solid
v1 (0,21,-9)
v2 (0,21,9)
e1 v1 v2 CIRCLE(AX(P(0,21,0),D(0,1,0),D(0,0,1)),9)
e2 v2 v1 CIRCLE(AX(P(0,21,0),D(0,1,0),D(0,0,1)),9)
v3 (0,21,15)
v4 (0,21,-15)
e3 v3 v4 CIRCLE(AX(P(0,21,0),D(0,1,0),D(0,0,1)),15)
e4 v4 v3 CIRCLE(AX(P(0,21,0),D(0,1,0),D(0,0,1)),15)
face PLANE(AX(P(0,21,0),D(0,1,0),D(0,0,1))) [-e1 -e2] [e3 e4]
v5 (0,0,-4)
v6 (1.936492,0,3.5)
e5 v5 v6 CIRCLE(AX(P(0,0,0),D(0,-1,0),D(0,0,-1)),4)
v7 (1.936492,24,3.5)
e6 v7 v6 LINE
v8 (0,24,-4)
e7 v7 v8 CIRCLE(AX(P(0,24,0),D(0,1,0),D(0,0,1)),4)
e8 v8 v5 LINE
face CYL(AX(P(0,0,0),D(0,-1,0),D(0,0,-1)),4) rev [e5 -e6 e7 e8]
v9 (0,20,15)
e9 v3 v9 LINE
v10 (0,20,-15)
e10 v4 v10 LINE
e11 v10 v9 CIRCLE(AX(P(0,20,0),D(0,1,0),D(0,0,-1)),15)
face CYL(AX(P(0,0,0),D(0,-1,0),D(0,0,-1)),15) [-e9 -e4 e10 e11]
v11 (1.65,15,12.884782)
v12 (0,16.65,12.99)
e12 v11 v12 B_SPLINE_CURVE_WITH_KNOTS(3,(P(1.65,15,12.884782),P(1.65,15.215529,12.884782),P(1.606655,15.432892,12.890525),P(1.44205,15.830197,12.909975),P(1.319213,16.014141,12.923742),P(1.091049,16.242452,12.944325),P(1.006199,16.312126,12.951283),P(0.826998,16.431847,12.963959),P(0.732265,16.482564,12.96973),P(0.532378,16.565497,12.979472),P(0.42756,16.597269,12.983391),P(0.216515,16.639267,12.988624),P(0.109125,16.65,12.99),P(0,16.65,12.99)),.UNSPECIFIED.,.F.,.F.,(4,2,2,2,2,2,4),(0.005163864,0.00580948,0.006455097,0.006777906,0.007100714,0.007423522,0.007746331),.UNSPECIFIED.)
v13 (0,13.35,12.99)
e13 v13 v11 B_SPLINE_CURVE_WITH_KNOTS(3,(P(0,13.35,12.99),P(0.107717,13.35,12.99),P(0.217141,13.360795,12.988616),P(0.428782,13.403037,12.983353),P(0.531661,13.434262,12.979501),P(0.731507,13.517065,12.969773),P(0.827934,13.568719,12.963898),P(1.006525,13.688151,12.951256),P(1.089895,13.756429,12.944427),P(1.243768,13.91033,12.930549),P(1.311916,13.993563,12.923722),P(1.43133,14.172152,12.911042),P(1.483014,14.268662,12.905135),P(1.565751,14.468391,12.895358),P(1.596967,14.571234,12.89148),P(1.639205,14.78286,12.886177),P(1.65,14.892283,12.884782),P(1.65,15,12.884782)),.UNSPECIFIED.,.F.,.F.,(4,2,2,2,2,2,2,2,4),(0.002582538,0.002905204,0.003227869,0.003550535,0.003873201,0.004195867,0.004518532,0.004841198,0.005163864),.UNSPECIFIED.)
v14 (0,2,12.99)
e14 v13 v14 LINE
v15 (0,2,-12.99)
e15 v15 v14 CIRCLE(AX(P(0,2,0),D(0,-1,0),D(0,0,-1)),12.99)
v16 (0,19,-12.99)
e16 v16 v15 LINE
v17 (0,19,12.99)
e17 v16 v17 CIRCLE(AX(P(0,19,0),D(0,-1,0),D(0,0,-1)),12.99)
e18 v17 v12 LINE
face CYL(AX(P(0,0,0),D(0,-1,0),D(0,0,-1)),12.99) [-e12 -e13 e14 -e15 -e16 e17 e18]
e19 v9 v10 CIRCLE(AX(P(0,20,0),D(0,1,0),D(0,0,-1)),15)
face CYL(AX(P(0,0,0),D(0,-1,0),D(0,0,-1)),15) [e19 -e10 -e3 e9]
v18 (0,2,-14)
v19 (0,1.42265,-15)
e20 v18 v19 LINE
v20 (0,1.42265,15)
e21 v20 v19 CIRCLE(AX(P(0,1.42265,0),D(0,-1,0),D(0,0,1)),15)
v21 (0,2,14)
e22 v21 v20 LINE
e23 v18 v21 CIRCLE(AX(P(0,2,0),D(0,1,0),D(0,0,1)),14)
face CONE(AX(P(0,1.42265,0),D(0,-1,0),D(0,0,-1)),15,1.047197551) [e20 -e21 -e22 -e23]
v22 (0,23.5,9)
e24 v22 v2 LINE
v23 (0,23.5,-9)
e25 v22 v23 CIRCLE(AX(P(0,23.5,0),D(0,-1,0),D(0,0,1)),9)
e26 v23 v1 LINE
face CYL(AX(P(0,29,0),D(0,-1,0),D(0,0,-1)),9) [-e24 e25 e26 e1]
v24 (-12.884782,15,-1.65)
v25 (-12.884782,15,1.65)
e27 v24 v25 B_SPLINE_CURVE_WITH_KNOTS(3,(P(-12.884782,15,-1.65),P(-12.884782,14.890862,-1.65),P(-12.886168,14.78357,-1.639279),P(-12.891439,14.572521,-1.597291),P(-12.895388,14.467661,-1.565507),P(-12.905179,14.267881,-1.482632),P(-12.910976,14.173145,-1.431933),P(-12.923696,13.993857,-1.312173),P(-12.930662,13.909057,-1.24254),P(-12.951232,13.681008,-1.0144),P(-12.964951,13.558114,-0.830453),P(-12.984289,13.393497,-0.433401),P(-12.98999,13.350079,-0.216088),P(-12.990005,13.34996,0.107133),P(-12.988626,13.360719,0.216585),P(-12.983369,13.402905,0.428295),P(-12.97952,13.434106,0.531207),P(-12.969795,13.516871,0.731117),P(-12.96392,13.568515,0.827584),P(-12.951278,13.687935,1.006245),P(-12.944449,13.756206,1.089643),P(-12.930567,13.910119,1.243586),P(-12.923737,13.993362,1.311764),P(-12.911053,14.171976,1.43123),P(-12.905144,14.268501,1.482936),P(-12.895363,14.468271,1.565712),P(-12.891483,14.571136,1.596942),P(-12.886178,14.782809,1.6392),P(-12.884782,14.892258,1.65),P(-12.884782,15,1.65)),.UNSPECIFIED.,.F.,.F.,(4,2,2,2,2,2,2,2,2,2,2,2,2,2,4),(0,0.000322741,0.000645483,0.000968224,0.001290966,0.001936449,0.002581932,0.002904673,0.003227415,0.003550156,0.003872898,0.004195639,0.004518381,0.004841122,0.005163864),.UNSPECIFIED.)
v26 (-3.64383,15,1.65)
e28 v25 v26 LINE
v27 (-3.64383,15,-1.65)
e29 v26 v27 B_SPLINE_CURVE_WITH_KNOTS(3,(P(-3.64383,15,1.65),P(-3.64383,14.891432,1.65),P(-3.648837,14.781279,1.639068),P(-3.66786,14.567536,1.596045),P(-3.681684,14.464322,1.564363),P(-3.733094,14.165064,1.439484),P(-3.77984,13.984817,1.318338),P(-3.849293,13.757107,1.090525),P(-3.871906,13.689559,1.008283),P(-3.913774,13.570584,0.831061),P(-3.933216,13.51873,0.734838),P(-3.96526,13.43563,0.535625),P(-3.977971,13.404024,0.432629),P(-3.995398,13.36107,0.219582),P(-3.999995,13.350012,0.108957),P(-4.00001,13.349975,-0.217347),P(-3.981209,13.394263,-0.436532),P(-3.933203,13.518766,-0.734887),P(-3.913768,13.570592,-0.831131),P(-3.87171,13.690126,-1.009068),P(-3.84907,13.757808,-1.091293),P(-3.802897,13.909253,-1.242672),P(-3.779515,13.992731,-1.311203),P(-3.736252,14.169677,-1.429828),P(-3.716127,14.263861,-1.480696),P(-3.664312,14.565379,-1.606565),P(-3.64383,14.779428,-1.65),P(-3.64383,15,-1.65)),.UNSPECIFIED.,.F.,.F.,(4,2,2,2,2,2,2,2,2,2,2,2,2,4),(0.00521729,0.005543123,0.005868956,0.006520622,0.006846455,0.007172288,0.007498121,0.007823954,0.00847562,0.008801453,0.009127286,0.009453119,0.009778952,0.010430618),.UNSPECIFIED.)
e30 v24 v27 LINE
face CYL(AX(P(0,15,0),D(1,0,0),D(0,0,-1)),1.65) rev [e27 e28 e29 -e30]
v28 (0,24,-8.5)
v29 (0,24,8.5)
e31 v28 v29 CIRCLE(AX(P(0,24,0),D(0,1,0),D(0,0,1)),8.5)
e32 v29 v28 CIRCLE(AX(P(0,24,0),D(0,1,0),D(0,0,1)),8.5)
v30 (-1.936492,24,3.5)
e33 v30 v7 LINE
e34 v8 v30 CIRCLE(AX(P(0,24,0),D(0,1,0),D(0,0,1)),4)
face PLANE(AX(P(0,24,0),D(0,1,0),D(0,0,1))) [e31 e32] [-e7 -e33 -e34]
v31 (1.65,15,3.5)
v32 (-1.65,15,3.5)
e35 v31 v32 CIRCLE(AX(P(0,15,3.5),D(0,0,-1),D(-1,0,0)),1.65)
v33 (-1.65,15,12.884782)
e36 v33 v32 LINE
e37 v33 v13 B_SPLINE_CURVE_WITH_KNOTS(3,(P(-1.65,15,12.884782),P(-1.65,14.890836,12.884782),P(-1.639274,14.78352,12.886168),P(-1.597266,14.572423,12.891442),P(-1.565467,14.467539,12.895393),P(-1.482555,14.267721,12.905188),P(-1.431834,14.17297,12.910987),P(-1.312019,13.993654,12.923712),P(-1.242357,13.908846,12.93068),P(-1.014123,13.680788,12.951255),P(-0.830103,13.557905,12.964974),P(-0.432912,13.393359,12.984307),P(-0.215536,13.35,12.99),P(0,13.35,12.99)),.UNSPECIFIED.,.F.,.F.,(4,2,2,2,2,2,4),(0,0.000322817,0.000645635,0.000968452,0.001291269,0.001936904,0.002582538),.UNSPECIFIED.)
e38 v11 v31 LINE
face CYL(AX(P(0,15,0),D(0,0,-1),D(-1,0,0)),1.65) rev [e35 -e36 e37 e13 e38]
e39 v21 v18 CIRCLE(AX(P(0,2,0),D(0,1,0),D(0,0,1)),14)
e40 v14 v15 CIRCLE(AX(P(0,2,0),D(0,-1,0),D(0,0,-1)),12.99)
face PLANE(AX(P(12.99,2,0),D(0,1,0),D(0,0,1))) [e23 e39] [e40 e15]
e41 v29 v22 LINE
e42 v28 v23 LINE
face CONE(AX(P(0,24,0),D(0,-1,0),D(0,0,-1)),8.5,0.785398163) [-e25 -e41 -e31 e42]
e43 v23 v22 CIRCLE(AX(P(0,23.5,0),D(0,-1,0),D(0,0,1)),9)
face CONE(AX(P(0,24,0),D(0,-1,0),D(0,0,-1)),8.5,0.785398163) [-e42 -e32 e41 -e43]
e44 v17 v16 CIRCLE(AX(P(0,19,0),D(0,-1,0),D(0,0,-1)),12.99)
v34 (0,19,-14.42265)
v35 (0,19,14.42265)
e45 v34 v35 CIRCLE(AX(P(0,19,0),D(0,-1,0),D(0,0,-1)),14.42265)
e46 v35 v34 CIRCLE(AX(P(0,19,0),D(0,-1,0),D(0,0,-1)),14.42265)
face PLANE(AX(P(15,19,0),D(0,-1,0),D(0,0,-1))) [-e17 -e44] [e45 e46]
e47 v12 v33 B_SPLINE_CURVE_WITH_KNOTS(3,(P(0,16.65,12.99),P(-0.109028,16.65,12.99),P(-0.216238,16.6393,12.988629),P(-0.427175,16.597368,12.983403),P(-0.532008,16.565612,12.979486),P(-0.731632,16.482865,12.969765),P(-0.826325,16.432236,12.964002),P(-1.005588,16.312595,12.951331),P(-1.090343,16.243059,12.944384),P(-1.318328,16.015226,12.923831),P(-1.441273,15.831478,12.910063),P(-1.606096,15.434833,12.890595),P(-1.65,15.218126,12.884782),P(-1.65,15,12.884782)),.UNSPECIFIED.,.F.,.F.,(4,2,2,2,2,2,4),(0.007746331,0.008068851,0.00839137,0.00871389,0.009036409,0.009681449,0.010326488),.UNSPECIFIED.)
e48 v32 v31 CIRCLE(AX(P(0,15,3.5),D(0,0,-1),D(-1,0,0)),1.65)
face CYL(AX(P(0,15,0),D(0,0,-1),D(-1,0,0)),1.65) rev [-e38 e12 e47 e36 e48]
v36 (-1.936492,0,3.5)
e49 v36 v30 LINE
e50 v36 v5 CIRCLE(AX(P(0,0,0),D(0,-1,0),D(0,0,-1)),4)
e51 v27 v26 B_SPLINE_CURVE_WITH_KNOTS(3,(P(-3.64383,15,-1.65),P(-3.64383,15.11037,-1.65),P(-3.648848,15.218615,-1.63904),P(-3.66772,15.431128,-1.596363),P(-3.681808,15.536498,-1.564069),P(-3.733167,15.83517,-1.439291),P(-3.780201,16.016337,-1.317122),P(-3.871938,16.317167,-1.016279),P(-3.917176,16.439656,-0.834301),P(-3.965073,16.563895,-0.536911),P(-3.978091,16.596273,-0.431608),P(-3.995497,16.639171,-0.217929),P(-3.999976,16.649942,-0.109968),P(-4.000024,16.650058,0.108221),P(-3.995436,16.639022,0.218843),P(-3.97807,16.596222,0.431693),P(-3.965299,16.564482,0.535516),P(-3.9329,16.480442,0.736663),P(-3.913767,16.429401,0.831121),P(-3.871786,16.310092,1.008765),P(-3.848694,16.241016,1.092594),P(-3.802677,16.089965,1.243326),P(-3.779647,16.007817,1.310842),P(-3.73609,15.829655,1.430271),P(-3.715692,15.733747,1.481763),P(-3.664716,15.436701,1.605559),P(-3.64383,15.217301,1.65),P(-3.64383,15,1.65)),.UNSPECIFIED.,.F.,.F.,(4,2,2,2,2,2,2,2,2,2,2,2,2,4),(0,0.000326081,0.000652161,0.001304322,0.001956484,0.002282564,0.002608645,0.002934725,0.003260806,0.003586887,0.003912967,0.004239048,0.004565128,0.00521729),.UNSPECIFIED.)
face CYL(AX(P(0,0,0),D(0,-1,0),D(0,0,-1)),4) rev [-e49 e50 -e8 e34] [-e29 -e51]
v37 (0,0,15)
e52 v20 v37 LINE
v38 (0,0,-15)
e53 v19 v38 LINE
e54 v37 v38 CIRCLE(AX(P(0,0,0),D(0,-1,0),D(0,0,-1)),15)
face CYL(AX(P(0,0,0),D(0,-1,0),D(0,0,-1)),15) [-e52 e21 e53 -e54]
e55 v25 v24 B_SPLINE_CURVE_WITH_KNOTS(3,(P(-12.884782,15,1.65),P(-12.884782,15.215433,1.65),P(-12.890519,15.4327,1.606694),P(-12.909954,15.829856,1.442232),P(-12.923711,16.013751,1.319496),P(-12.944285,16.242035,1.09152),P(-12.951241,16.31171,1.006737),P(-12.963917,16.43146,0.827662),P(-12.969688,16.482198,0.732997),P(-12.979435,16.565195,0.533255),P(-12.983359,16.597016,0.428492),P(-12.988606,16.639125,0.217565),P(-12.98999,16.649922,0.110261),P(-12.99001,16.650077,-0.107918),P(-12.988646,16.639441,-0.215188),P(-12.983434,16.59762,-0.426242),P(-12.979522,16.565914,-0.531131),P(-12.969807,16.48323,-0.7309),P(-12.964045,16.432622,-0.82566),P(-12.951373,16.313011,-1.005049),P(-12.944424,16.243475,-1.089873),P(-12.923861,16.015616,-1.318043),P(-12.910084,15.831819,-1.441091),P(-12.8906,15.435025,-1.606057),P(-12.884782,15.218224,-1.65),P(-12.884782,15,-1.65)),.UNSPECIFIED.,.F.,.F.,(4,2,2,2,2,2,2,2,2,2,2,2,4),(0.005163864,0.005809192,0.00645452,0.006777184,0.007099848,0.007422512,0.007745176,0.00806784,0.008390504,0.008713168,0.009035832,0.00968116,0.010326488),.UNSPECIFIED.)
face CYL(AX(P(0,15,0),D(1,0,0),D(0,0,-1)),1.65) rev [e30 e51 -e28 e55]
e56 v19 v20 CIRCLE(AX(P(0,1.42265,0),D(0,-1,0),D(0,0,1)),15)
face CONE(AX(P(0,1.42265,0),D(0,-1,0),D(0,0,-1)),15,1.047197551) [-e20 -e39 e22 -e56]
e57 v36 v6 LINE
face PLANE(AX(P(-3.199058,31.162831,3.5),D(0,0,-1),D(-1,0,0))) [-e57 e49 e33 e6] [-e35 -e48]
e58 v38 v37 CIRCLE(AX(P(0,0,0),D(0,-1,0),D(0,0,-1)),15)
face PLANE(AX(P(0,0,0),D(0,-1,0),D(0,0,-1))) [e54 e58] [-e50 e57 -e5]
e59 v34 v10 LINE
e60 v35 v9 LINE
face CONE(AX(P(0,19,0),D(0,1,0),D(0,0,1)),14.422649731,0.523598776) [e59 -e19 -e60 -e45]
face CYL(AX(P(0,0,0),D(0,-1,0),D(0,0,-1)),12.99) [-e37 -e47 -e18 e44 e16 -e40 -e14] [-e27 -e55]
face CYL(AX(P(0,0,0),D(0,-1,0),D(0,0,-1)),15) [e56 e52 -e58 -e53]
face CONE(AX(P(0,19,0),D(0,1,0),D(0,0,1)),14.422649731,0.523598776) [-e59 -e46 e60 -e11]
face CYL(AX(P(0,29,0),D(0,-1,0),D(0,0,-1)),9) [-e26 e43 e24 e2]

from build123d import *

# Parameters (mm, degrees)
SKETCH_5_R               = 20.566311538
CUT_EXTRUDE_1_DEPTH      = 0.5
SKETCH_6_R               = 21.52826295
CUT_EXTRUDE_2_DEPTH      = 0.5
EXTRUDE_START            = 11
SKETCH_7_R               = 8.5
SKETCH_7_R_2             = 4
EXTRUDE_1_DEPTH          = 11
SKETCH_10_R              = 15
CUT_EXTRUDE_3_DEPTH      = 15
SKETCH_11_R              = 15
SKETCH_11_R_2            = 4
EXTRUDE_2_DEPTH          = 0.5
EXTRUDE_START_2          = 0.5
SKETCH_12_R              = 15
SKETCH_12_R_2            = 4
EXTRUDE_3_DEPTH          = 0.5
EXTRUDE_START_3          = 8
SKETCH_14_R              = 7
SKETCH_14_R_2            = 4
EXTRUDE_5_DEPTH          = 8
SKETCH_17_R              = 17.215216586
CUT_EXTRUDE_4_DEPTH      = 30.849623113
SKETCH_18_R              = 9
SKETCH_18_R_2            = 4
EXTRUDE_6_DEPTH          = 8
CHAMFER_1_SIZE           = 1
CHAMFER_1_SIZE2          = 0.577350269
CHAMFER_2_SIZE           = 1
CHAMFER_2_SIZE2          = 0.577350269
CHAMFER_3_SIZE           = 0.5
SKETCH_22_R              = 10.406041916
CUT_EXTRUDE_6_DEPTH      = 5
SKETCH_24_W              = 7.050057501
SKETCH_24_H              = 1.266031453
EXTRUDE_7_DEPTH          = 24
SKETCH_19_W              = 1.65
SKETCH_19_H              = 15
PATTERN_CIRCULAR_1_COUNT = 2
PATTERN_CIRCULAR_1_ANGLE = 90
CHAMFER_4_SIZE           = 0.5


with BuildPart() as part:
    # 草图1 → 旋转1 (revolve)
    with BuildSketch(Plane.XY, mode=Mode.PRIVATE) as revolve_1_sk:
        Polygon((4, 0), (4, 21), (15, 21), (15, 19), (12.99, 19), (12.99, 2), (15, 2), (15, 0), align=None)
    revolve(revolve_1_sk.sketch.rotate(Axis((0, 0, 0), (0, 1, 0)), 90), axis=Axis((0, 0, 0), (0, 1, 0)))

    # 草图5 → 切除-拉伸1 (cut)
    with BuildSketch(Plane.XZ):
        Circle(SKETCH_5_R)
    extrude(amount=-CUT_EXTRUDE_1_DEPTH, mode=Mode.SUBTRACT)

    # 草图6 → 切除-拉伸2 (cut)
    with BuildSketch(Plane(origin=(0, 21, 0), x_dir=(1, 0, 0), z_dir=(0, 1, 0))):
        Circle(SKETCH_6_R)
    extrude(amount=-CUT_EXTRUDE_2_DEPTH, mode=Mode.SUBTRACT)

    # 草图7 → 凸台-拉伸1 (add)
    with BuildSketch(Plane(origin=(0, 20.5, 0), x_dir=(1, 0, 0), z_dir=(0, 1, 0)).offset(EXTRUDE_START)):
        with Locations(Location((0, 0, 0), (0, 0, 270))):
            Circle(SKETCH_7_R)
        with Locations(Location((0, 0, 0), (0, 0, 90))):
            Circle(SKETCH_7_R_2, mode=Mode.SUBTRACT)
    extrude(amount=-EXTRUDE_1_DEPTH)

    # 草图10 → 切除-拉伸3 (cut)
    with BuildSketch(Plane(origin=(0, 20.5, 0), x_dir=(1, 0, 0), z_dir=(0, 1, 0))):
        with Locations(Location((0, 0, 0), (0, 0, 90))):
            Circle(SKETCH_10_R)
    extrude(amount=CUT_EXTRUDE_3_DEPTH, mode=Mode.SUBTRACT)

    # 草图11 → 凸台-拉伸2 (add)
    with BuildSketch(Plane(origin=(0, 20.5, 0), x_dir=(1, 0, 0), z_dir=(0, 1, 0))):
        with Locations(Location((0, 0, 0), (0, 0, 90))):
            Circle(SKETCH_11_R)
        with Locations(Location((0, 0, 0), (0, 0, 90))):
            Circle(SKETCH_11_R_2, mode=Mode.SUBTRACT)
    extrude(amount=EXTRUDE_2_DEPTH)

    # 草图12 → 凸台-拉伸3 (add)
    with BuildSketch(Plane.XZ.offset(-0.5).offset(EXTRUDE_START_2)):
        with Locations(Location((0, 0, 0), (0, 0, 270))):
            Circle(SKETCH_12_R)
        with Locations(Location((0, 0, 0), (0, 0, 270))):
            Circle(SKETCH_12_R_2, mode=Mode.SUBTRACT)
    extrude(amount=-EXTRUDE_3_DEPTH)

    # 草图14 → 凸台-拉伸5 (add)
    with BuildSketch(Plane(origin=(0, 21, 0), x_dir=(1, 0, 0), z_dir=(0, 1, 0)).offset(EXTRUDE_START_3)):
        with Locations(Location((0, 0, 0), (0, 0, 270))):
            Circle(SKETCH_14_R)
        with Locations(Location((0, 0, 0), (0, 0, 90))):
            Circle(SKETCH_14_R_2, mode=Mode.SUBTRACT)
    extrude(amount=-EXTRUDE_5_DEPTH)

    # 草图17 → 切除-拉伸4 (cut, through all)
    with BuildSketch(Plane(origin=(0, 21, 0), x_dir=(1, 0, 0), z_dir=(0, 1, 0))):
        Circle(SKETCH_17_R)
    extrude(amount=CUT_EXTRUDE_4_DEPTH, mode=Mode.SUBTRACT)

    # 草图18 → 凸台-拉伸6 (add)
    with BuildSketch(Plane(origin=(0, 21, 0), x_dir=(1, 0, 0), z_dir=(0, 1, 0)).offset(EXTRUDE_START_3)):
        with Locations(Location((0, 0, 0), (0, 0, 270))):
            Circle(SKETCH_18_R)
        with Locations(Location((0, 0, 0), (0, 0, 90))):
            Circle(SKETCH_18_R_2, mode=Mode.SUBTRACT)
    extrude(amount=-EXTRUDE_6_DEPTH)

    # 倒角1
    chamfer_1_edges = [part.edges().sort_by_distance(p)[0] for p in [
        (0, 19, 15),
    ]]
    chamfer_1_side = [part.faces().sort_by_distance(p)[0] for p in [
        (0, 20, 15),
    ]]
    chamfer(chamfer_1_edges, length=CHAMFER_1_SIZE, length2=CHAMFER_1_SIZE2, reference=chamfer_1_side[0])

    # 倒角2
    chamfer_2_edges = [part.edges().sort_by_distance(p)[0] for p in [
        (0, 2, 15),
    ]]
    chamfer_2_side = [part.faces().sort_by_distance(p)[0] for p in [
        (0, 2, 13.414264069),
    ]]
    chamfer(chamfer_2_edges, length=CHAMFER_2_SIZE, length2=CHAMFER_2_SIZE2, reference=chamfer_2_side[0])

    # 倒角3
    chamfer_3_edges = [part.edges().sort_by_distance(p)[0] for p in [
        (0, 29, -9),
    ]]
    chamfer(chamfer_3_edges, length=CHAMFER_3_SIZE)

    # 草图22 → 切除-拉伸6 (cut)
    with BuildSketch(Plane(origin=(0, 29, 0), x_dir=(1, 0, 0), z_dir=(0, 1, 0))):
        Circle(SKETCH_22_R)
    extrude(amount=-CUT_EXTRUDE_6_DEPTH, mode=Mode.SUBTRACT)

    # 草图24 → 凸台-拉伸7 (add)
    with BuildSketch(Plane.XZ):
        with Locations((0.325970853, 4.133015727)):
            Rectangle(SKETCH_24_W, SKETCH_24_H)
    extrude(amount=-EXTRUDE_7_DEPTH)

    # 草图19 → M4 螺纹孔1 (revolve, cut)
    with BuildSketch(Plane(origin=(0, 15, 0), x_dir=(0, 1, 0), z_dir=(1, 0, 0))):
        with Locations((0.825, 7.5)):
            Rectangle(SKETCH_19_W, SKETCH_19_H)
    hole_wizard_m4_1 = revolve(axis=Axis((0, 15, -6.35), (0, 0, 1)), mode=Mode.SUBTRACT)

    # 阵列(圆周)1: M4 螺纹孔1 ×2 about axis
    pattern_circular_1_axis = Axis((0, 0, 0), (0, -1, 0))
    for i in range(1, PATTERN_CIRCULAR_1_COUNT):
        add(hole_wizard_m4_1.rotate(pattern_circular_1_axis, i * PATTERN_CIRCULAR_1_ANGLE / (PATTERN_CIRCULAR_1_COUNT - 1)), mode=Mode.SUBTRACT)

    # 倒角4
    chamfer_4_edges = [part.edges().sort_by_distance(p)[0] for p in [
        (0, 24, -9),
    ]]
    chamfer(chamfer_4_edges, length=CHAMFER_4_SIZE)


solid = part.part
